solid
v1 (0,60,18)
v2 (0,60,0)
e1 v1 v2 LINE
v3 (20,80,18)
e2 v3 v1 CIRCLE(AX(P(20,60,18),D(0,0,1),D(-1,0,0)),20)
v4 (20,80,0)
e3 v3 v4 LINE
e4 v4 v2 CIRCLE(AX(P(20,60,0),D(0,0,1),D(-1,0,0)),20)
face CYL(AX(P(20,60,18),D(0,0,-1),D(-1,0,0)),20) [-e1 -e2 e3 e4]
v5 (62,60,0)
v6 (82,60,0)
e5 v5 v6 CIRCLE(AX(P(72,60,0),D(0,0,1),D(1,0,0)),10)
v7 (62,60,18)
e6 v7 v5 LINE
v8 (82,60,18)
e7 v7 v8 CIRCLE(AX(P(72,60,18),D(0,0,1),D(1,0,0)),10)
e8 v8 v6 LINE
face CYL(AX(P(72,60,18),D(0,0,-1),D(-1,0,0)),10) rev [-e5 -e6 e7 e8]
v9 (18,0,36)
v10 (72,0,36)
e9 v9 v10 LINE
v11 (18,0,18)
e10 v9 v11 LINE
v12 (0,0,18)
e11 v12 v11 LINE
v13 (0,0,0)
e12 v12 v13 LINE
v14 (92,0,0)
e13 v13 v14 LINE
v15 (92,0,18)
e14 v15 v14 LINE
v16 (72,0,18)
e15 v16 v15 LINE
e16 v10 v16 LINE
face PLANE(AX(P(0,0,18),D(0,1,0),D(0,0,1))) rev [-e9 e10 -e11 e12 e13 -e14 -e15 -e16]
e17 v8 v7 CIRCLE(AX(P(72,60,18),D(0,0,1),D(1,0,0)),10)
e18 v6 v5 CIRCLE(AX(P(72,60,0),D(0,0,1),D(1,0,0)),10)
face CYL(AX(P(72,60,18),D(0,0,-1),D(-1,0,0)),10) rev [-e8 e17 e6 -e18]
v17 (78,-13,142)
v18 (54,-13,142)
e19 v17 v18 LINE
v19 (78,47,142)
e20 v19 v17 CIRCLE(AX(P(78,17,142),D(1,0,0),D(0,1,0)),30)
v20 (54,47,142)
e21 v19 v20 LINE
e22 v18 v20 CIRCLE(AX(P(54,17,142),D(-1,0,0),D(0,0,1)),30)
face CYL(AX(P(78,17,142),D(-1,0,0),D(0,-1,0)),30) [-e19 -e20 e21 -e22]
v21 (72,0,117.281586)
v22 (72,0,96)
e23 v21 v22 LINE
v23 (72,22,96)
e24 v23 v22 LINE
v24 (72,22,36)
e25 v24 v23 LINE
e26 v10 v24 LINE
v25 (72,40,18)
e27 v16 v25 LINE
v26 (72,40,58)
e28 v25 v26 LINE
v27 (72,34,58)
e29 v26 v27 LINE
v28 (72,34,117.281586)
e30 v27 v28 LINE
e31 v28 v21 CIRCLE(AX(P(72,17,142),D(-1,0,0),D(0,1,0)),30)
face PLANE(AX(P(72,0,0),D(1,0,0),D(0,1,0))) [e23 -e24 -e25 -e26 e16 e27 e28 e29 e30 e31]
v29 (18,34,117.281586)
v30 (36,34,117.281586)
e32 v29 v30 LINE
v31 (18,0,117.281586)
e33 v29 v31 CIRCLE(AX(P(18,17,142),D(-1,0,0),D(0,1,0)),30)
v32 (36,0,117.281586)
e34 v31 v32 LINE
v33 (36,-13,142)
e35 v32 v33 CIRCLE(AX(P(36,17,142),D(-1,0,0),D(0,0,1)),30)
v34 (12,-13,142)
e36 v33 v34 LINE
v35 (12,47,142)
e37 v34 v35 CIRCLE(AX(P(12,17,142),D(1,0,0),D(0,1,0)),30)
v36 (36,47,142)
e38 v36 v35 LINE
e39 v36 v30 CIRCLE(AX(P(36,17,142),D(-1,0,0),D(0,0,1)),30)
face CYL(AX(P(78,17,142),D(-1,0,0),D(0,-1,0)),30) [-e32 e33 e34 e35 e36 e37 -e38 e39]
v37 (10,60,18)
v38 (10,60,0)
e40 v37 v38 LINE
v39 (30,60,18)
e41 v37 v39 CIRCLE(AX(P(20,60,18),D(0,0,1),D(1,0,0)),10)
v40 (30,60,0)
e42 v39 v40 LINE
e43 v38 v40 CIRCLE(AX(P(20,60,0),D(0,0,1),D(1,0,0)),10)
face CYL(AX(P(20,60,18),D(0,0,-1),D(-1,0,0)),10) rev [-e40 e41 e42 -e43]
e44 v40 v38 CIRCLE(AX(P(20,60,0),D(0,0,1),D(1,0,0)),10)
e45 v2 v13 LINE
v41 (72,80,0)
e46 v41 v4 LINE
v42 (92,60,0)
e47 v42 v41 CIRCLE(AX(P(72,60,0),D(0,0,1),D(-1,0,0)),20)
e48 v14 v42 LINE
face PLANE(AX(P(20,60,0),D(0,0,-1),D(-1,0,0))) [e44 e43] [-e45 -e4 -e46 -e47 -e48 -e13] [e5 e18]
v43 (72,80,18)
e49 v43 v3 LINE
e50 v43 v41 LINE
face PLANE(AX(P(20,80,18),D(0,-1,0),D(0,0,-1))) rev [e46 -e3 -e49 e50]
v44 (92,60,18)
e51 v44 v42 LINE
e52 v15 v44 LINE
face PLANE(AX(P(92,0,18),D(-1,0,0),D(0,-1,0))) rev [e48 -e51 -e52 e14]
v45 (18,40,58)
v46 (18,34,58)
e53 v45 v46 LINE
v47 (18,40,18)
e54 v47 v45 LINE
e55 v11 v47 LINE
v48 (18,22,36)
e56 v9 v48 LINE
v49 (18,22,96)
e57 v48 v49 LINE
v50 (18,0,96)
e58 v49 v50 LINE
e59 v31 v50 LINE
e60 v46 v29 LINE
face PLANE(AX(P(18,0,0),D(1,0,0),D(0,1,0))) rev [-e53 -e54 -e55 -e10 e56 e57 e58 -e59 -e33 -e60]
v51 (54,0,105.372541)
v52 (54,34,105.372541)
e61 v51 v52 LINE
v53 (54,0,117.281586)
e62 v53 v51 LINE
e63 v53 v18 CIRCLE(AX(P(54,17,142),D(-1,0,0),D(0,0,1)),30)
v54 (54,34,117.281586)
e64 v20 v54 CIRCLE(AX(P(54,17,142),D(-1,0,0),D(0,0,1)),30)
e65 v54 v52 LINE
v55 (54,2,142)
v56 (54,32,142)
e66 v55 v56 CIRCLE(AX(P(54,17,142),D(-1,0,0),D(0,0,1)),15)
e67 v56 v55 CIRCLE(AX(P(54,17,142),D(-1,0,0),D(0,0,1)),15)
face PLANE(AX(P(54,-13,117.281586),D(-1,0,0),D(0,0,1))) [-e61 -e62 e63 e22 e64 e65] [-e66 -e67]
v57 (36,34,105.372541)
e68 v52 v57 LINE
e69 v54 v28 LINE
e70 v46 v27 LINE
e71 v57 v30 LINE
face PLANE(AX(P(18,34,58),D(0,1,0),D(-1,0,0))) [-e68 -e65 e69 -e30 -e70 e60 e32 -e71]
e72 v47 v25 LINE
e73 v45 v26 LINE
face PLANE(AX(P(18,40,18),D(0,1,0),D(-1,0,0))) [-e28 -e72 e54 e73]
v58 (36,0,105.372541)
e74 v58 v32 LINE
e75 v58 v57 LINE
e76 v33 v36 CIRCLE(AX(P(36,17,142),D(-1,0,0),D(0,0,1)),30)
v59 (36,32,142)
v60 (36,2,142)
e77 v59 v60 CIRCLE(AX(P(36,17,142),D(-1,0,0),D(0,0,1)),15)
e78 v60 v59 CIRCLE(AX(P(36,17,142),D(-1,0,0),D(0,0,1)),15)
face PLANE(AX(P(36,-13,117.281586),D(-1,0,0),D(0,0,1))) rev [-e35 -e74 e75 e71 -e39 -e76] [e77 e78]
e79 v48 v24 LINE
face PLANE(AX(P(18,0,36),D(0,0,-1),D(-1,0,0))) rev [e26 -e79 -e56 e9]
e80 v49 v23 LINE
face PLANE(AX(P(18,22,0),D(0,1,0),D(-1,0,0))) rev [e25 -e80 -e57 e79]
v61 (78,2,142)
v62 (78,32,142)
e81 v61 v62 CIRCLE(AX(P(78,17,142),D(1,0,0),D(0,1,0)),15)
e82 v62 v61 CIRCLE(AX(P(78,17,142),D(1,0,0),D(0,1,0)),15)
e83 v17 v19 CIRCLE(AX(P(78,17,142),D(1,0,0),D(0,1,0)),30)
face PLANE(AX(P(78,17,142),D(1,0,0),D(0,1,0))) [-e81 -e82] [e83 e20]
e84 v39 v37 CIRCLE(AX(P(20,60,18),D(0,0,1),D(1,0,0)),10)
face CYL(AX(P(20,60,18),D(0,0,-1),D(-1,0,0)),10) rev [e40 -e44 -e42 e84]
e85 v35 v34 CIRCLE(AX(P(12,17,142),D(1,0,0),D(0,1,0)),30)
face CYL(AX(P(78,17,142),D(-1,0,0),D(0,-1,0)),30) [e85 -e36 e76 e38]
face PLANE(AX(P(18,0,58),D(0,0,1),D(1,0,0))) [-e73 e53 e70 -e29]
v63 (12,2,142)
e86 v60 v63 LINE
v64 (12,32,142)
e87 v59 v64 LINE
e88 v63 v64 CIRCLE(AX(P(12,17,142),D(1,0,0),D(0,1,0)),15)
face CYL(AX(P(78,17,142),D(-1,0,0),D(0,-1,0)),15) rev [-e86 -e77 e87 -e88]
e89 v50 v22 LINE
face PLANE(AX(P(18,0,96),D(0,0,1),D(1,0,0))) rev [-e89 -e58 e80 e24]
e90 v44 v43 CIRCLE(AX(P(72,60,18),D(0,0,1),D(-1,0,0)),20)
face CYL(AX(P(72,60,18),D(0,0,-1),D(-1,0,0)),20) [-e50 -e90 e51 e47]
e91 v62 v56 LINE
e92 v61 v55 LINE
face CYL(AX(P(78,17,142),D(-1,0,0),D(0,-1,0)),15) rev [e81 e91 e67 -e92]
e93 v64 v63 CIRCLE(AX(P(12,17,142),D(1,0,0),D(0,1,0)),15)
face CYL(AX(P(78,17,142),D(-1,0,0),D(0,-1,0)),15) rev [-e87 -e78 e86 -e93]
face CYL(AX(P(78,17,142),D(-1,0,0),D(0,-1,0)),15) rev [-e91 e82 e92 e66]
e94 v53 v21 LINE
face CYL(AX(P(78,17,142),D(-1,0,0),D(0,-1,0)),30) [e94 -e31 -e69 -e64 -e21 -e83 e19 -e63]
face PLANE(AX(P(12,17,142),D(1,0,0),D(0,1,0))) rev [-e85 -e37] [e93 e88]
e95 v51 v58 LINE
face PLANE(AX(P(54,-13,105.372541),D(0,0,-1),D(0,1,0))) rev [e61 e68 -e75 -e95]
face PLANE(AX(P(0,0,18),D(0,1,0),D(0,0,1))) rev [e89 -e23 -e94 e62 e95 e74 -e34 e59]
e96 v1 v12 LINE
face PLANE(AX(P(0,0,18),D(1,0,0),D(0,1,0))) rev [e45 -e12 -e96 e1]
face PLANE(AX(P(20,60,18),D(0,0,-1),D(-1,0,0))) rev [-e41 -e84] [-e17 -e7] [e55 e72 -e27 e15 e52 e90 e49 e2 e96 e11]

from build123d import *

# Parameters (mm, degrees)
MOUNTING_PLATE_SKETCH_R       = 10
MOUNTING_PLATE_DEPTH          = 18
ARM_START                     = -20
ARM_SKETCH_40X40_W            = 40
ARM_SKETCH_40X40_H            = 40
ARM_BOSS_DEPTH                = 54
ARM_EXTENSION_SKETCH_W        = 62
ARM_EXTENSION_SKETCH_H        = 34
ARM_EXTENSION_DEPTH           = 54
ARM_RECESS_SKETCH_W           = 60
ARM_RECESS_SKETCH_H           = 22
ARM_RECESS_CUT_DEPTH          = 54
STEP_PAD_DEPTH                = 6
STEP_PAD_DEPTH_BACK           = 60
STEP_PAD_SKETCH_R             = 30
STEP_PAD_SKETCH_R_2           = 15
CLEVIS_PROFILE_CUT_DEPTH      = 211.82694325
CLEVIS_PROFILE_CUT_DEPTH_BACK = 211.82694325
CLEVIS_PROFILE_SKETCH_W       = 18
CLEVIS_PROFILE_SKETCH_H       = 63.461103314
CLEVIS_SLOT_CUT_DEPTH         = 201.641471286
CLEVIS_SLOT_CUT_DEPTH_BACK    = 201.641471286
CLEVIS_SLOT_SKETCH_W          = 18
CLEVIS_SLOT_SKETCH_H          = 11.909045211


with BuildPart() as part:
    # Mounting Plate Sketch → Mounting Plate (new body)
    with BuildSketch(Plane.XY):
        with BuildLine():
            Line((0, 0), (92, 0))
            Line((92, 0), (92, 60))
            ThreePointArc((92, 60), (86.142135624, 74.142135624), (72, 80))
            Line((72, 80), (20, 80))
            ThreePointArc((20, 80), (5.857864376, 74.142135624), (0, 60))
            Line((0, 60), (0, 0))
        make_face()
        with Locations((20, 60)):
            Circle(MOUNTING_PLATE_SKETCH_R, mode=Mode.SUBTRACT)
        with Locations((72, 60)):
            Circle(MOUNTING_PLATE_SKETCH_R, mode=Mode.SUBTRACT)
    extrude(amount=MOUNTING_PLATE_DEPTH)

    # Arm Sketch 40x40 → Arm Boss (add)
    with BuildSketch(Plane(origin=(92, 0, 0), x_dir=(0, 0, -1), z_dir=(1, 0, 0)).offset(ARM_START)):
        with Locations((-38, 20)):
            Rectangle(ARM_SKETCH_40X40_W, ARM_SKETCH_40X40_H)
    extrude(amount=-ARM_BOSS_DEPTH)

    # Arm Extension Sketch → Arm Extension (add)
    with BuildSketch(Plane(origin=(72, 0, 0), x_dir=(0, 0, -1), z_dir=(1, 0, 0))):
        with Locations((-89, 17)):
            Rectangle(ARM_EXTENSION_SKETCH_W, ARM_EXTENSION_SKETCH_H)
    extrude(amount=-ARM_EXTENSION_DEPTH)

    # Arm Recess Sketch → Arm Recess Cut (cut)
    with BuildSketch(Plane(origin=(72, 0, 0), x_dir=(0, 0, -1), z_dir=(1, 0, 0))):
        with Locations((-66, 11)):
            Rectangle(ARM_RECESS_SKETCH_W, ARM_RECESS_SKETCH_H)
    extrude(amount=-ARM_RECESS_CUT_DEPTH, mode=Mode.SUBTRACT)

    # Step Pad Sketch → Step Pad (add, two sides: drawn at the far end of the back side and taken through both)
    with BuildSketch(Plane(origin=(72, 0, 0), x_dir=(0, 0, -1), z_dir=(1, 0, 0)).offset(-STEP_PAD_DEPTH_BACK)):
        with Locations(Location((-142, 17, 0), (0, 0, 90))):
            Circle(STEP_PAD_SKETCH_R)
        with Locations(Location((-142, 17, 0), (0, 0, 90))):
            Circle(STEP_PAD_SKETCH_R_2, mode=Mode.SUBTRACT)
    extrude(amount=STEP_PAD_DEPTH + STEP_PAD_DEPTH_BACK)

    # Clevis Profile Sketch → Clevis Profile Cut (cut, two sides: drawn at the far end of the back side and taken through both)
    with BuildSketch(Plane(origin=(0, 0, 0), x_dir=(1, 0, 0), z_dir=(0, 1, 0)).offset(-CLEVIS_PROFILE_CUT_DEPTH_BACK)):
        with Locations((45, -149.012137468)):
            Rectangle(CLEVIS_PROFILE_SKETCH_W, CLEVIS_PROFILE_SKETCH_H)
    extrude(amount=CLEVIS_PROFILE_CUT_DEPTH + CLEVIS_PROFILE_CUT_DEPTH_BACK, mode=Mode.SUBTRACT)

    # Clevis Slot Sketch → Clevis Slot Cut (cut, two sides: drawn at the far end of the back side and taken through both)
    with BuildSketch(Plane(origin=(0, 34, 0), x_dir=(1, 0, 0), z_dir=(0, 1, 0)).offset(-CLEVIS_SLOT_CUT_DEPTH_BACK)):
        with Locations((45, -111.327063206)):
            Rectangle(CLEVIS_SLOT_SKETCH_W, CLEVIS_SLOT_SKETCH_H)
    extrude(amount=CLEVIS_SLOT_CUT_DEPTH + CLEVIS_SLOT_CUT_DEPTH_BACK, mode=Mode.SUBTRACT)


solid = part.part
